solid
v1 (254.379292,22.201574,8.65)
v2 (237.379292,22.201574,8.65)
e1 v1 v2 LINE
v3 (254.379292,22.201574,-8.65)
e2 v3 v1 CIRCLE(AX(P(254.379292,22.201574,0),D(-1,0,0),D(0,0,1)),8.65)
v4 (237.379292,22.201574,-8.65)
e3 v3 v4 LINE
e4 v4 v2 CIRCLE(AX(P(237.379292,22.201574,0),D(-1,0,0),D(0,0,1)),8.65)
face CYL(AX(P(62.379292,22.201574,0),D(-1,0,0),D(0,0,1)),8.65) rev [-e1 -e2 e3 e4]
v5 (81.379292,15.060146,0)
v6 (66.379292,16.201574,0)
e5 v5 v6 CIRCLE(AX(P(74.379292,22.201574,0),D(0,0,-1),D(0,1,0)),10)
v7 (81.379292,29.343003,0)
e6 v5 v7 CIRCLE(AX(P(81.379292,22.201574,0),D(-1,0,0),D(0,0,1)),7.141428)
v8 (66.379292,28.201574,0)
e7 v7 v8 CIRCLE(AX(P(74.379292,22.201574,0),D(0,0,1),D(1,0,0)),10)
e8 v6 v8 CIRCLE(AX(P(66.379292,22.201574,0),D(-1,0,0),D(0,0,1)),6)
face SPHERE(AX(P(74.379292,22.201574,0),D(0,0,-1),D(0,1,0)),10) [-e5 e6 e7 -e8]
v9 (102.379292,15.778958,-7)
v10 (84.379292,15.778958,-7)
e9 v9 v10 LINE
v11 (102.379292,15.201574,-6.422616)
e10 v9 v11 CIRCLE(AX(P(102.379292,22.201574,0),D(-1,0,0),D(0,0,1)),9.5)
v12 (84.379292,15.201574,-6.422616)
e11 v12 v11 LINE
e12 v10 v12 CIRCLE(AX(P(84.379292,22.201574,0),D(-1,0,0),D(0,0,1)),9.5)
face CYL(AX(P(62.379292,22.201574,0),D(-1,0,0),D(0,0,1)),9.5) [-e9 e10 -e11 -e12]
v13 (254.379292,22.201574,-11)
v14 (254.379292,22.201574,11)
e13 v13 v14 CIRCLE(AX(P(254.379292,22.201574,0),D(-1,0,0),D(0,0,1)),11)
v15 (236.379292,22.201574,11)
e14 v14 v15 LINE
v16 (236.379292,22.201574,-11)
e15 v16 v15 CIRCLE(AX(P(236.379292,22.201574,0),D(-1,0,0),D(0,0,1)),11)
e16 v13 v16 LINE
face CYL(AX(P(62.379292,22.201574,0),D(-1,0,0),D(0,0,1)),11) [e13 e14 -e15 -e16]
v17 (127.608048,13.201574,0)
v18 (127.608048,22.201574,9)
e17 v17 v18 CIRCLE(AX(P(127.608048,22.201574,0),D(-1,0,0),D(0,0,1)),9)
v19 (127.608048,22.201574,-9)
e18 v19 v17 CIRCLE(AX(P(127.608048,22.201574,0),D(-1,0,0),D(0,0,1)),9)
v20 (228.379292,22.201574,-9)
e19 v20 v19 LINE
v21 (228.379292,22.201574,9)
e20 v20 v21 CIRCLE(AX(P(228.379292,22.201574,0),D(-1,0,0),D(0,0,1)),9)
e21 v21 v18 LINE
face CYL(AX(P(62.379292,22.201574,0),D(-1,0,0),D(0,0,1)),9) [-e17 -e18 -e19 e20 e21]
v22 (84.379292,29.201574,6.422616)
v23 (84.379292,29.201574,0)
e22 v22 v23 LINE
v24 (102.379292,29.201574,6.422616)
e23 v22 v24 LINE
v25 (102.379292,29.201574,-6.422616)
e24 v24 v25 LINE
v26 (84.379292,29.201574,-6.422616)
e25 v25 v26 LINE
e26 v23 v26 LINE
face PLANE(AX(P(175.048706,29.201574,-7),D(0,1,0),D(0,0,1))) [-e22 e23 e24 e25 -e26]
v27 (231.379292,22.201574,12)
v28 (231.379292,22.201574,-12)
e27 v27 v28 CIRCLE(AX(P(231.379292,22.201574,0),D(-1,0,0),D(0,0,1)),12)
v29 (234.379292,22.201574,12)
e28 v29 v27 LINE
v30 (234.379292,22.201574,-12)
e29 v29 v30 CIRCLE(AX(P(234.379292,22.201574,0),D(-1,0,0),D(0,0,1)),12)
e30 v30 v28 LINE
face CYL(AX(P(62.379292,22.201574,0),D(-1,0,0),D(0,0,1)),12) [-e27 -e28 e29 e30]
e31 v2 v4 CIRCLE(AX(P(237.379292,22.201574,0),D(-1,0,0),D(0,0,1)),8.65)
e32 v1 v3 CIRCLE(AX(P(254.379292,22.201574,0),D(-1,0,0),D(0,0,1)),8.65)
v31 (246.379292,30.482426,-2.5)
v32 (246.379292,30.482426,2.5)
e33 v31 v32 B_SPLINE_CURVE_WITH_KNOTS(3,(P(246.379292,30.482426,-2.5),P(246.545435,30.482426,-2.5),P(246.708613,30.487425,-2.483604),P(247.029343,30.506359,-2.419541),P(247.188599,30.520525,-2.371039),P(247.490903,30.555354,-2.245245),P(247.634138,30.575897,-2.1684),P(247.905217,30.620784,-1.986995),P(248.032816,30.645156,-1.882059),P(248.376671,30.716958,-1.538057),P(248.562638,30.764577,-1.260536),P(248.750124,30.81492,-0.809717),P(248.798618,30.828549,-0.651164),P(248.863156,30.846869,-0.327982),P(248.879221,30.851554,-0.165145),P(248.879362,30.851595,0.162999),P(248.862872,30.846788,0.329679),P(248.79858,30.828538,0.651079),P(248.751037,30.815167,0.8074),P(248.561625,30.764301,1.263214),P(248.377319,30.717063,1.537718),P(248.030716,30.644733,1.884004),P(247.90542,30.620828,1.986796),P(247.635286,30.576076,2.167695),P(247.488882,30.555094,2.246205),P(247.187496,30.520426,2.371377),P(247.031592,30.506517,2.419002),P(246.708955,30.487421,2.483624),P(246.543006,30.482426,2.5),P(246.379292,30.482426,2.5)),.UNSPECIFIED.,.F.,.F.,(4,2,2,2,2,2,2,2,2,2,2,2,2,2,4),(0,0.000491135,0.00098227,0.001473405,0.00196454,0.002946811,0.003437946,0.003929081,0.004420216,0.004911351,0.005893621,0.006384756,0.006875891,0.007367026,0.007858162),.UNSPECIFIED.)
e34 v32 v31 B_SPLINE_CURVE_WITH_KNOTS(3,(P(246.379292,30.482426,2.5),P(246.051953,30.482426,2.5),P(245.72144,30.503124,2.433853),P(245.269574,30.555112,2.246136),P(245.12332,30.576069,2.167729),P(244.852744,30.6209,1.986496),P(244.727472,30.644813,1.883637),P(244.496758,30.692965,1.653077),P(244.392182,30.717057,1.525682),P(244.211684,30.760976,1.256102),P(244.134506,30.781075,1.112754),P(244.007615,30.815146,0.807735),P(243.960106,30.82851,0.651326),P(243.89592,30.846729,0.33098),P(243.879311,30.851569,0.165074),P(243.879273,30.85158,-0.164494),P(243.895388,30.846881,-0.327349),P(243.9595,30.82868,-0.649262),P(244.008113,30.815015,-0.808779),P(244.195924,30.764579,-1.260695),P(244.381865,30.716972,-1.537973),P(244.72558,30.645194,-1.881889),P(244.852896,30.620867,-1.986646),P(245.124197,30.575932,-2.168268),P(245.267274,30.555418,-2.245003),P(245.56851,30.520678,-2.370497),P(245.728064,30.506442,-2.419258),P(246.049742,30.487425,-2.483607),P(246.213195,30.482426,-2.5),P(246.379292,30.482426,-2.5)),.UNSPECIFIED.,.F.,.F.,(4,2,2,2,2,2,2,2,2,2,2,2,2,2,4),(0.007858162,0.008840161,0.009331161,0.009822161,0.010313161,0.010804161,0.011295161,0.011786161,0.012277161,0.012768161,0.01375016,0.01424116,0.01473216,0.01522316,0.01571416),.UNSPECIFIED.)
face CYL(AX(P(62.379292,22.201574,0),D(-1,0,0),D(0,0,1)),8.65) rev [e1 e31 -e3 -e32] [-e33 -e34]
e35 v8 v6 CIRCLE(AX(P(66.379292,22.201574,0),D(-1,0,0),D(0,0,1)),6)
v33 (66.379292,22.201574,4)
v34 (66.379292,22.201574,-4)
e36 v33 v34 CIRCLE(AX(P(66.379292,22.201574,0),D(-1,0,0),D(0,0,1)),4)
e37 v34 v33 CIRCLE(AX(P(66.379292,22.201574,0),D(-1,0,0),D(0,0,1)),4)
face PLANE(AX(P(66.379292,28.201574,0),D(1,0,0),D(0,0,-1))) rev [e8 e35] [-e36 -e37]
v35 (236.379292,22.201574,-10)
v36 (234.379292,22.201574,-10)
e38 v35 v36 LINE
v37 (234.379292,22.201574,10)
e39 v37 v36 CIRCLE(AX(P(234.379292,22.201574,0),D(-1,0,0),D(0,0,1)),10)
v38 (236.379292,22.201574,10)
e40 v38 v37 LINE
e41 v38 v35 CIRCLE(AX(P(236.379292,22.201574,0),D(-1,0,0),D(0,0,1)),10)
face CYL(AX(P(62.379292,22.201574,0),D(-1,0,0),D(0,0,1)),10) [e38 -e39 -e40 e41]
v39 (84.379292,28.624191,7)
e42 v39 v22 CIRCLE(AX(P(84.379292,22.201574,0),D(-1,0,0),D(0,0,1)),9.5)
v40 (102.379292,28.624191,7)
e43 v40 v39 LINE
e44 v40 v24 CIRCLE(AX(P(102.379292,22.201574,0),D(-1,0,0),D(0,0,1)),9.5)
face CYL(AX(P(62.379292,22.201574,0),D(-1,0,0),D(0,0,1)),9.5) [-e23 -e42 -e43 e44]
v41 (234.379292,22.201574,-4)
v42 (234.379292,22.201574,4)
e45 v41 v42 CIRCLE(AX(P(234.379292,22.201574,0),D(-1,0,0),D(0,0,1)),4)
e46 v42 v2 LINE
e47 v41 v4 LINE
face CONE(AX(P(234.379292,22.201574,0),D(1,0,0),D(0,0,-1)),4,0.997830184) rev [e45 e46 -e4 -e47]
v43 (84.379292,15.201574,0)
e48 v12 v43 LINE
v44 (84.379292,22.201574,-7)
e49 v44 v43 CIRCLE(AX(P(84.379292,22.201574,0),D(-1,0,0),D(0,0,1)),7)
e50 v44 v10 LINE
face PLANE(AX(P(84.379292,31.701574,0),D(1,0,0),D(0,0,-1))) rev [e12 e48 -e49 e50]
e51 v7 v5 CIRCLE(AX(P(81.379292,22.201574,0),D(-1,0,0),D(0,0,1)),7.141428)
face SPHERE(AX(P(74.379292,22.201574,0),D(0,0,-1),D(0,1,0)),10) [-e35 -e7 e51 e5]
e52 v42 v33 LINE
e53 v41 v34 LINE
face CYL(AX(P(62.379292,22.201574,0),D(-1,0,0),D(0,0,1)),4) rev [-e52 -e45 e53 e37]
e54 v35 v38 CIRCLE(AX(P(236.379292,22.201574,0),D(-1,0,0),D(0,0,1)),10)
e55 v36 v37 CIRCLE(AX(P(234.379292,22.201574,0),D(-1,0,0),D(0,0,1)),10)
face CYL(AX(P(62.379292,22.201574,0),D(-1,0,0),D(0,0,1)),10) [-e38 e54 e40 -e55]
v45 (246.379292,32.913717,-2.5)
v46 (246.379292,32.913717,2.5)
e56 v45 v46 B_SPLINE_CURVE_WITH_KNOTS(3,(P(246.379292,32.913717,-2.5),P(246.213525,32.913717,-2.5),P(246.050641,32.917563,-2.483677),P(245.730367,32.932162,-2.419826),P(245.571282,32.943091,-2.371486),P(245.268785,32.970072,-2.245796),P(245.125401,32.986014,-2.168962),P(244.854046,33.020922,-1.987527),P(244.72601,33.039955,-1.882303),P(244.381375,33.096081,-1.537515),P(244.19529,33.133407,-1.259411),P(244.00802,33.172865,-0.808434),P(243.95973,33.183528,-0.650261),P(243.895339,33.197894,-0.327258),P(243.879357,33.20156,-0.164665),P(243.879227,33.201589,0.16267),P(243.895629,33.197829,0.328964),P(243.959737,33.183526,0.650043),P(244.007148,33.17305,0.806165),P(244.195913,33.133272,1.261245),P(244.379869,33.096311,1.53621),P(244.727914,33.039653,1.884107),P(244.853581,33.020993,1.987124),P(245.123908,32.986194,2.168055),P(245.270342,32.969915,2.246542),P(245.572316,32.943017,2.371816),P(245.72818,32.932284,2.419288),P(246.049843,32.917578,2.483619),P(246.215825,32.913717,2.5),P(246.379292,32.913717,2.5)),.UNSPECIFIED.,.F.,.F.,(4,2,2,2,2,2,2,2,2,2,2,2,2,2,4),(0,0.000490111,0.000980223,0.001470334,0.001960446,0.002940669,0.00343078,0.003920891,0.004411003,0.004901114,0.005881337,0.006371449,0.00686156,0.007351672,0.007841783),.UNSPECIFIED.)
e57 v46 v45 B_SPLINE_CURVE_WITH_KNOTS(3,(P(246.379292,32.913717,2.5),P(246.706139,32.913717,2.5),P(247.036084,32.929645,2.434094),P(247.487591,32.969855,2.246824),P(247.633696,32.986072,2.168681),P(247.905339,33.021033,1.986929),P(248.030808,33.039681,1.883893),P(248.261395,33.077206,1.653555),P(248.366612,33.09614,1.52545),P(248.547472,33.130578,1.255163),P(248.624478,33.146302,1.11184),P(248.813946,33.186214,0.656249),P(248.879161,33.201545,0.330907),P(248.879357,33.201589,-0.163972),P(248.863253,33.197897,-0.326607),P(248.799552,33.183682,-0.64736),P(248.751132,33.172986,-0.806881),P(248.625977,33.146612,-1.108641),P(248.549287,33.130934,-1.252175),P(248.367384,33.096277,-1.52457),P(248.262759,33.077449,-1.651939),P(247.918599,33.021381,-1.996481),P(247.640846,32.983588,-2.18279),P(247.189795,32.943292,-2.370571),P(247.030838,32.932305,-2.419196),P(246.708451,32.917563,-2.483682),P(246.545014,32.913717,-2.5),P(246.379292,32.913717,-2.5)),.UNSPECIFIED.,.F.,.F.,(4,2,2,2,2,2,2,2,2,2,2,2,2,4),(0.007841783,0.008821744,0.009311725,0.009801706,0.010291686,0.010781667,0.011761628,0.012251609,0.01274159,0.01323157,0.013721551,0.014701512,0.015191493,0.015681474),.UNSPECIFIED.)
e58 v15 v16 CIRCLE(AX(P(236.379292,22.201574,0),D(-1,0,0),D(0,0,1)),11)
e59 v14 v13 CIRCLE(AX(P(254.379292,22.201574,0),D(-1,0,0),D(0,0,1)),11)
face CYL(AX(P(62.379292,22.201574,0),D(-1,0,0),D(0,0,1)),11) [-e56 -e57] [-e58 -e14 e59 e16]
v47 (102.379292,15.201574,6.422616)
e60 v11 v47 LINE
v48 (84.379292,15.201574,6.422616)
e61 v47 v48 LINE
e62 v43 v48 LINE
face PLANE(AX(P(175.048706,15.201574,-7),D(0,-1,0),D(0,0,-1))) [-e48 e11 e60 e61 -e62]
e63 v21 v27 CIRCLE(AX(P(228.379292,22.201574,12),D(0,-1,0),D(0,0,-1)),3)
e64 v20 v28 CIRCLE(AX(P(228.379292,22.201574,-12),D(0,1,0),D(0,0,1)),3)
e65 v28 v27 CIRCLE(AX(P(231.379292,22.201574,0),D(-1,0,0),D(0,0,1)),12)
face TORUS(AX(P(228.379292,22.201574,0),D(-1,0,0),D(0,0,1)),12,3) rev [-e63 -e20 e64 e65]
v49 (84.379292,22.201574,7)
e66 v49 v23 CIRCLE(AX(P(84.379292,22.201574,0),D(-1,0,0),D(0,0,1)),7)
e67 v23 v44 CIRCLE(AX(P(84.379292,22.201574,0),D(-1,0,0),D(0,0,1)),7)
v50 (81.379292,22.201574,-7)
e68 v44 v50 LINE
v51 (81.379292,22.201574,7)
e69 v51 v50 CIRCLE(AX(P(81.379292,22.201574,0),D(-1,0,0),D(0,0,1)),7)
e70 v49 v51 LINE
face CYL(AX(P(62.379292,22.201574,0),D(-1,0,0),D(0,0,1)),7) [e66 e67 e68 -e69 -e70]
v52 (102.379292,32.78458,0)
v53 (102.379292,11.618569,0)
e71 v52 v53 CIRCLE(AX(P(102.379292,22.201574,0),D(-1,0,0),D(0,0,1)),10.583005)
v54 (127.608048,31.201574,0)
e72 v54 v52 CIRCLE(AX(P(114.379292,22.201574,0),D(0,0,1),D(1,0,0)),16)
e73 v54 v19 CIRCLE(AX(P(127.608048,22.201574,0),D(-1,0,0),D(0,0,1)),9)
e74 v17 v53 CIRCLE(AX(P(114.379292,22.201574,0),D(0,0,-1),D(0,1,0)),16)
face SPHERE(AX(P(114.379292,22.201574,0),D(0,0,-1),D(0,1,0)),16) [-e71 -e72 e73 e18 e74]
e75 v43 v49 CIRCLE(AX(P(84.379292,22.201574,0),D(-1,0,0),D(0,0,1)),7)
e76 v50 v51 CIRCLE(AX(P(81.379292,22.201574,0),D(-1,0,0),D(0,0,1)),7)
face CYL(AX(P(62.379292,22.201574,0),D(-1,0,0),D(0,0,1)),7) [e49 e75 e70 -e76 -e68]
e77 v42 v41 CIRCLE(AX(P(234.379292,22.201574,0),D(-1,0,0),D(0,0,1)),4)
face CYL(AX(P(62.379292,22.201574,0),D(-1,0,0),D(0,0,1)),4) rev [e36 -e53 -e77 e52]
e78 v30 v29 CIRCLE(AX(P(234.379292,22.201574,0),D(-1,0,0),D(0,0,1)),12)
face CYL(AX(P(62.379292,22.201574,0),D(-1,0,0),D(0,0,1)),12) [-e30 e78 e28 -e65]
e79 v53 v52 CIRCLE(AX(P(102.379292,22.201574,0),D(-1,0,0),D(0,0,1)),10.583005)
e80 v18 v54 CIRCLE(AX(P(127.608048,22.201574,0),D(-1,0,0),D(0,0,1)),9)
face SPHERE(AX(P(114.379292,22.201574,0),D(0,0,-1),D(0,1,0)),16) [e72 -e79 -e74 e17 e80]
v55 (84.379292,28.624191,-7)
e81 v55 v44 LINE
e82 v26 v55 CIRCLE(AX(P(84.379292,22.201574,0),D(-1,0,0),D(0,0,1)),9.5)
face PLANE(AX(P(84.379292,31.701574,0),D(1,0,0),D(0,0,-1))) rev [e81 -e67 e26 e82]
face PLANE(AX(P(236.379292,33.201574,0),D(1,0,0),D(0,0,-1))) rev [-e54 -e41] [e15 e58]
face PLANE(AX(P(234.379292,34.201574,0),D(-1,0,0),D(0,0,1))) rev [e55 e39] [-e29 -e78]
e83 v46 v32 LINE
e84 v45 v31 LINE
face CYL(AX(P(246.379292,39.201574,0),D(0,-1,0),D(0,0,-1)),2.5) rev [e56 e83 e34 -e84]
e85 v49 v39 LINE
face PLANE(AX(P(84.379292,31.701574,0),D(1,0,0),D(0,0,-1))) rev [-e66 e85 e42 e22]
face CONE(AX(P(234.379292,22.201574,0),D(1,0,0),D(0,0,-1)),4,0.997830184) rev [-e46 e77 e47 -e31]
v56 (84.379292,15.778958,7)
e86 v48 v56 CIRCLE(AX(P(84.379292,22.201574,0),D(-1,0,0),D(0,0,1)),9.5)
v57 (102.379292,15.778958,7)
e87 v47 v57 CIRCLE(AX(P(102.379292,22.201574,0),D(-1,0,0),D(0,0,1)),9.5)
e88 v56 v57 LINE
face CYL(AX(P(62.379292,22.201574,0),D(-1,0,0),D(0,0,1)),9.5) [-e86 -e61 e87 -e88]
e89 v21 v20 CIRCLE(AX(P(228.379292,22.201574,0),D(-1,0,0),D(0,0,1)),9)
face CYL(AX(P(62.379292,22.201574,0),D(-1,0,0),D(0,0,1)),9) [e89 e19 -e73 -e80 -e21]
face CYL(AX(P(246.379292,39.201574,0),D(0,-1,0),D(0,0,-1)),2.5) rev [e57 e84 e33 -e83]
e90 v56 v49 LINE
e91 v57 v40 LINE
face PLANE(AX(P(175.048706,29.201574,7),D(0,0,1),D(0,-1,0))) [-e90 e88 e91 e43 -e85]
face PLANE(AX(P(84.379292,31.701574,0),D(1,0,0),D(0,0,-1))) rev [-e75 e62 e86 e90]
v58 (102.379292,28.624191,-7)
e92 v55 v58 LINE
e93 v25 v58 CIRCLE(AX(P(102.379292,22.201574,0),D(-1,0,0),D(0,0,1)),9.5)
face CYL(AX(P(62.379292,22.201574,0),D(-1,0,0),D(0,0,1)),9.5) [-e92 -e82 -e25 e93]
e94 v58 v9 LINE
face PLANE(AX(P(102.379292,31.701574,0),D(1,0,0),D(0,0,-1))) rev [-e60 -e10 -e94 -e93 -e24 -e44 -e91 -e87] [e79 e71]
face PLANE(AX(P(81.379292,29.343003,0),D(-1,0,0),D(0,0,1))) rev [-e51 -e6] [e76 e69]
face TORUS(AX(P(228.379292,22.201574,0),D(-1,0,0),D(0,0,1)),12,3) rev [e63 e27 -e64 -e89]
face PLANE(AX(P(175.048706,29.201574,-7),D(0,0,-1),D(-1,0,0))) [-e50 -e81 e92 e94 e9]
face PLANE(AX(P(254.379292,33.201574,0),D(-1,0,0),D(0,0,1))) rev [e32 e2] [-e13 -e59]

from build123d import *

# Parameters (mm, degrees)
SKETCH2_R          = 25.69251773
SKETCH2_W          = 14
SKETCH2_H          = 14
CUT_EXTRUDE1_DEPTH = 18
SKETCH4_R          = 2.5
CUT_EXTRUDE3_DEPTH = 10


with BuildPart() as part:
    # Sketch1 → Revolve1 (revolve)
    with BuildSketch(Plane.XY, mode=Mode.PRIVATE) as revolve1_sk:
        with BuildLine():
            Line((254.379291769, 33.201574447), (254.379291769, 30.851574447))
            Line((254.379291769, 30.851574447), (237.379291769, 30.851574447))
            Line((237.379291769, 30.851574447), (234.379291769, 26.201574447))
            Line((234.379291769, 26.201574447), (172.647910202, 26.201574447))
            Line((172.647910202, 26.201574447), (66.379291769, 26.201574447))
            Line((66.379291769, 26.201574447), (66.379291769, 28.201574447))
            ThreePointArc((66.379291769, 28.201574447), (73.620533102, 32.172747161), (81.379291769, 29.343002876))
            Line((81.379291769, 29.343002876), (81.379291769, 29.201574447))
            Line((81.379291769, 29.201574447), (84.379291769, 29.201574447))
            Line((84.379291769, 29.201574447), (84.379291769, 31.701574447))
            Line((84.379291769, 31.701574447), (102.379291769, 31.701574447))
            Line((102.379291769, 31.701574447), (102.379291769, 32.784579692))
            ThreePointArc((102.379291769, 32.784579692), (115.381258369, 38.170170595), (127.608048324, 31.201574447))
            Line((127.608048324, 31.201574447), (228.379291769, 31.201574447))
            ThreePointArc((228.379291769, 31.201574447), (230.500612112, 32.080254104), (231.379291769, 34.201574447))
            Line((231.379291769, 34.201574447), (234.379291769, 34.201574447))
            Line((234.379291769, 34.201574447), (234.379291769, 32.201574447))
            Line((234.379291769, 32.201574447), (236.379291769, 32.201574447))
            Line((236.379291769, 32.201574447), (236.379291769, 33.201574447))
            Line((236.379291769, 33.201574447), (254.379291769, 33.201574447))
        make_face()
    revolve(revolve1_sk.sketch.rotate(Axis((62.379291769, 22.201574447, 0), (1, 0, 0)), 90), axis=Axis((62.379291769, 22.201574447, 0), (1, 0, 0)))

    # Sketch2 → Cut-Extrude1 (cut)
    with BuildSketch(Plane.ZY.offset(-84.379291769)):
        with Locations((0, 22.201574447)):
            Circle(SKETCH2_R)
        with Locations((0, 22.201574447)):
            Rectangle(SKETCH2_W, SKETCH2_H, mode=Mode.SUBTRACT)
    extrude(amount=-CUT_EXTRUDE1_DEPTH, mode=Mode.SUBTRACT)

    # Sketch4 → Cut-Extrude3 (cut)
    with BuildSketch(Plane(origin=(0, 29.201574447, 0), x_dir=(1, 0, 0), z_dir=(0, 1, 0))):
        with Locations(Location((246.379291769, 0, 0), (0, 0, 90))):
            Circle(SKETCH4_R)
    extrude(amount=CUT_EXTRUDE3_DEPTH, mode=Mode.SUBTRACT)


solid = part.part
